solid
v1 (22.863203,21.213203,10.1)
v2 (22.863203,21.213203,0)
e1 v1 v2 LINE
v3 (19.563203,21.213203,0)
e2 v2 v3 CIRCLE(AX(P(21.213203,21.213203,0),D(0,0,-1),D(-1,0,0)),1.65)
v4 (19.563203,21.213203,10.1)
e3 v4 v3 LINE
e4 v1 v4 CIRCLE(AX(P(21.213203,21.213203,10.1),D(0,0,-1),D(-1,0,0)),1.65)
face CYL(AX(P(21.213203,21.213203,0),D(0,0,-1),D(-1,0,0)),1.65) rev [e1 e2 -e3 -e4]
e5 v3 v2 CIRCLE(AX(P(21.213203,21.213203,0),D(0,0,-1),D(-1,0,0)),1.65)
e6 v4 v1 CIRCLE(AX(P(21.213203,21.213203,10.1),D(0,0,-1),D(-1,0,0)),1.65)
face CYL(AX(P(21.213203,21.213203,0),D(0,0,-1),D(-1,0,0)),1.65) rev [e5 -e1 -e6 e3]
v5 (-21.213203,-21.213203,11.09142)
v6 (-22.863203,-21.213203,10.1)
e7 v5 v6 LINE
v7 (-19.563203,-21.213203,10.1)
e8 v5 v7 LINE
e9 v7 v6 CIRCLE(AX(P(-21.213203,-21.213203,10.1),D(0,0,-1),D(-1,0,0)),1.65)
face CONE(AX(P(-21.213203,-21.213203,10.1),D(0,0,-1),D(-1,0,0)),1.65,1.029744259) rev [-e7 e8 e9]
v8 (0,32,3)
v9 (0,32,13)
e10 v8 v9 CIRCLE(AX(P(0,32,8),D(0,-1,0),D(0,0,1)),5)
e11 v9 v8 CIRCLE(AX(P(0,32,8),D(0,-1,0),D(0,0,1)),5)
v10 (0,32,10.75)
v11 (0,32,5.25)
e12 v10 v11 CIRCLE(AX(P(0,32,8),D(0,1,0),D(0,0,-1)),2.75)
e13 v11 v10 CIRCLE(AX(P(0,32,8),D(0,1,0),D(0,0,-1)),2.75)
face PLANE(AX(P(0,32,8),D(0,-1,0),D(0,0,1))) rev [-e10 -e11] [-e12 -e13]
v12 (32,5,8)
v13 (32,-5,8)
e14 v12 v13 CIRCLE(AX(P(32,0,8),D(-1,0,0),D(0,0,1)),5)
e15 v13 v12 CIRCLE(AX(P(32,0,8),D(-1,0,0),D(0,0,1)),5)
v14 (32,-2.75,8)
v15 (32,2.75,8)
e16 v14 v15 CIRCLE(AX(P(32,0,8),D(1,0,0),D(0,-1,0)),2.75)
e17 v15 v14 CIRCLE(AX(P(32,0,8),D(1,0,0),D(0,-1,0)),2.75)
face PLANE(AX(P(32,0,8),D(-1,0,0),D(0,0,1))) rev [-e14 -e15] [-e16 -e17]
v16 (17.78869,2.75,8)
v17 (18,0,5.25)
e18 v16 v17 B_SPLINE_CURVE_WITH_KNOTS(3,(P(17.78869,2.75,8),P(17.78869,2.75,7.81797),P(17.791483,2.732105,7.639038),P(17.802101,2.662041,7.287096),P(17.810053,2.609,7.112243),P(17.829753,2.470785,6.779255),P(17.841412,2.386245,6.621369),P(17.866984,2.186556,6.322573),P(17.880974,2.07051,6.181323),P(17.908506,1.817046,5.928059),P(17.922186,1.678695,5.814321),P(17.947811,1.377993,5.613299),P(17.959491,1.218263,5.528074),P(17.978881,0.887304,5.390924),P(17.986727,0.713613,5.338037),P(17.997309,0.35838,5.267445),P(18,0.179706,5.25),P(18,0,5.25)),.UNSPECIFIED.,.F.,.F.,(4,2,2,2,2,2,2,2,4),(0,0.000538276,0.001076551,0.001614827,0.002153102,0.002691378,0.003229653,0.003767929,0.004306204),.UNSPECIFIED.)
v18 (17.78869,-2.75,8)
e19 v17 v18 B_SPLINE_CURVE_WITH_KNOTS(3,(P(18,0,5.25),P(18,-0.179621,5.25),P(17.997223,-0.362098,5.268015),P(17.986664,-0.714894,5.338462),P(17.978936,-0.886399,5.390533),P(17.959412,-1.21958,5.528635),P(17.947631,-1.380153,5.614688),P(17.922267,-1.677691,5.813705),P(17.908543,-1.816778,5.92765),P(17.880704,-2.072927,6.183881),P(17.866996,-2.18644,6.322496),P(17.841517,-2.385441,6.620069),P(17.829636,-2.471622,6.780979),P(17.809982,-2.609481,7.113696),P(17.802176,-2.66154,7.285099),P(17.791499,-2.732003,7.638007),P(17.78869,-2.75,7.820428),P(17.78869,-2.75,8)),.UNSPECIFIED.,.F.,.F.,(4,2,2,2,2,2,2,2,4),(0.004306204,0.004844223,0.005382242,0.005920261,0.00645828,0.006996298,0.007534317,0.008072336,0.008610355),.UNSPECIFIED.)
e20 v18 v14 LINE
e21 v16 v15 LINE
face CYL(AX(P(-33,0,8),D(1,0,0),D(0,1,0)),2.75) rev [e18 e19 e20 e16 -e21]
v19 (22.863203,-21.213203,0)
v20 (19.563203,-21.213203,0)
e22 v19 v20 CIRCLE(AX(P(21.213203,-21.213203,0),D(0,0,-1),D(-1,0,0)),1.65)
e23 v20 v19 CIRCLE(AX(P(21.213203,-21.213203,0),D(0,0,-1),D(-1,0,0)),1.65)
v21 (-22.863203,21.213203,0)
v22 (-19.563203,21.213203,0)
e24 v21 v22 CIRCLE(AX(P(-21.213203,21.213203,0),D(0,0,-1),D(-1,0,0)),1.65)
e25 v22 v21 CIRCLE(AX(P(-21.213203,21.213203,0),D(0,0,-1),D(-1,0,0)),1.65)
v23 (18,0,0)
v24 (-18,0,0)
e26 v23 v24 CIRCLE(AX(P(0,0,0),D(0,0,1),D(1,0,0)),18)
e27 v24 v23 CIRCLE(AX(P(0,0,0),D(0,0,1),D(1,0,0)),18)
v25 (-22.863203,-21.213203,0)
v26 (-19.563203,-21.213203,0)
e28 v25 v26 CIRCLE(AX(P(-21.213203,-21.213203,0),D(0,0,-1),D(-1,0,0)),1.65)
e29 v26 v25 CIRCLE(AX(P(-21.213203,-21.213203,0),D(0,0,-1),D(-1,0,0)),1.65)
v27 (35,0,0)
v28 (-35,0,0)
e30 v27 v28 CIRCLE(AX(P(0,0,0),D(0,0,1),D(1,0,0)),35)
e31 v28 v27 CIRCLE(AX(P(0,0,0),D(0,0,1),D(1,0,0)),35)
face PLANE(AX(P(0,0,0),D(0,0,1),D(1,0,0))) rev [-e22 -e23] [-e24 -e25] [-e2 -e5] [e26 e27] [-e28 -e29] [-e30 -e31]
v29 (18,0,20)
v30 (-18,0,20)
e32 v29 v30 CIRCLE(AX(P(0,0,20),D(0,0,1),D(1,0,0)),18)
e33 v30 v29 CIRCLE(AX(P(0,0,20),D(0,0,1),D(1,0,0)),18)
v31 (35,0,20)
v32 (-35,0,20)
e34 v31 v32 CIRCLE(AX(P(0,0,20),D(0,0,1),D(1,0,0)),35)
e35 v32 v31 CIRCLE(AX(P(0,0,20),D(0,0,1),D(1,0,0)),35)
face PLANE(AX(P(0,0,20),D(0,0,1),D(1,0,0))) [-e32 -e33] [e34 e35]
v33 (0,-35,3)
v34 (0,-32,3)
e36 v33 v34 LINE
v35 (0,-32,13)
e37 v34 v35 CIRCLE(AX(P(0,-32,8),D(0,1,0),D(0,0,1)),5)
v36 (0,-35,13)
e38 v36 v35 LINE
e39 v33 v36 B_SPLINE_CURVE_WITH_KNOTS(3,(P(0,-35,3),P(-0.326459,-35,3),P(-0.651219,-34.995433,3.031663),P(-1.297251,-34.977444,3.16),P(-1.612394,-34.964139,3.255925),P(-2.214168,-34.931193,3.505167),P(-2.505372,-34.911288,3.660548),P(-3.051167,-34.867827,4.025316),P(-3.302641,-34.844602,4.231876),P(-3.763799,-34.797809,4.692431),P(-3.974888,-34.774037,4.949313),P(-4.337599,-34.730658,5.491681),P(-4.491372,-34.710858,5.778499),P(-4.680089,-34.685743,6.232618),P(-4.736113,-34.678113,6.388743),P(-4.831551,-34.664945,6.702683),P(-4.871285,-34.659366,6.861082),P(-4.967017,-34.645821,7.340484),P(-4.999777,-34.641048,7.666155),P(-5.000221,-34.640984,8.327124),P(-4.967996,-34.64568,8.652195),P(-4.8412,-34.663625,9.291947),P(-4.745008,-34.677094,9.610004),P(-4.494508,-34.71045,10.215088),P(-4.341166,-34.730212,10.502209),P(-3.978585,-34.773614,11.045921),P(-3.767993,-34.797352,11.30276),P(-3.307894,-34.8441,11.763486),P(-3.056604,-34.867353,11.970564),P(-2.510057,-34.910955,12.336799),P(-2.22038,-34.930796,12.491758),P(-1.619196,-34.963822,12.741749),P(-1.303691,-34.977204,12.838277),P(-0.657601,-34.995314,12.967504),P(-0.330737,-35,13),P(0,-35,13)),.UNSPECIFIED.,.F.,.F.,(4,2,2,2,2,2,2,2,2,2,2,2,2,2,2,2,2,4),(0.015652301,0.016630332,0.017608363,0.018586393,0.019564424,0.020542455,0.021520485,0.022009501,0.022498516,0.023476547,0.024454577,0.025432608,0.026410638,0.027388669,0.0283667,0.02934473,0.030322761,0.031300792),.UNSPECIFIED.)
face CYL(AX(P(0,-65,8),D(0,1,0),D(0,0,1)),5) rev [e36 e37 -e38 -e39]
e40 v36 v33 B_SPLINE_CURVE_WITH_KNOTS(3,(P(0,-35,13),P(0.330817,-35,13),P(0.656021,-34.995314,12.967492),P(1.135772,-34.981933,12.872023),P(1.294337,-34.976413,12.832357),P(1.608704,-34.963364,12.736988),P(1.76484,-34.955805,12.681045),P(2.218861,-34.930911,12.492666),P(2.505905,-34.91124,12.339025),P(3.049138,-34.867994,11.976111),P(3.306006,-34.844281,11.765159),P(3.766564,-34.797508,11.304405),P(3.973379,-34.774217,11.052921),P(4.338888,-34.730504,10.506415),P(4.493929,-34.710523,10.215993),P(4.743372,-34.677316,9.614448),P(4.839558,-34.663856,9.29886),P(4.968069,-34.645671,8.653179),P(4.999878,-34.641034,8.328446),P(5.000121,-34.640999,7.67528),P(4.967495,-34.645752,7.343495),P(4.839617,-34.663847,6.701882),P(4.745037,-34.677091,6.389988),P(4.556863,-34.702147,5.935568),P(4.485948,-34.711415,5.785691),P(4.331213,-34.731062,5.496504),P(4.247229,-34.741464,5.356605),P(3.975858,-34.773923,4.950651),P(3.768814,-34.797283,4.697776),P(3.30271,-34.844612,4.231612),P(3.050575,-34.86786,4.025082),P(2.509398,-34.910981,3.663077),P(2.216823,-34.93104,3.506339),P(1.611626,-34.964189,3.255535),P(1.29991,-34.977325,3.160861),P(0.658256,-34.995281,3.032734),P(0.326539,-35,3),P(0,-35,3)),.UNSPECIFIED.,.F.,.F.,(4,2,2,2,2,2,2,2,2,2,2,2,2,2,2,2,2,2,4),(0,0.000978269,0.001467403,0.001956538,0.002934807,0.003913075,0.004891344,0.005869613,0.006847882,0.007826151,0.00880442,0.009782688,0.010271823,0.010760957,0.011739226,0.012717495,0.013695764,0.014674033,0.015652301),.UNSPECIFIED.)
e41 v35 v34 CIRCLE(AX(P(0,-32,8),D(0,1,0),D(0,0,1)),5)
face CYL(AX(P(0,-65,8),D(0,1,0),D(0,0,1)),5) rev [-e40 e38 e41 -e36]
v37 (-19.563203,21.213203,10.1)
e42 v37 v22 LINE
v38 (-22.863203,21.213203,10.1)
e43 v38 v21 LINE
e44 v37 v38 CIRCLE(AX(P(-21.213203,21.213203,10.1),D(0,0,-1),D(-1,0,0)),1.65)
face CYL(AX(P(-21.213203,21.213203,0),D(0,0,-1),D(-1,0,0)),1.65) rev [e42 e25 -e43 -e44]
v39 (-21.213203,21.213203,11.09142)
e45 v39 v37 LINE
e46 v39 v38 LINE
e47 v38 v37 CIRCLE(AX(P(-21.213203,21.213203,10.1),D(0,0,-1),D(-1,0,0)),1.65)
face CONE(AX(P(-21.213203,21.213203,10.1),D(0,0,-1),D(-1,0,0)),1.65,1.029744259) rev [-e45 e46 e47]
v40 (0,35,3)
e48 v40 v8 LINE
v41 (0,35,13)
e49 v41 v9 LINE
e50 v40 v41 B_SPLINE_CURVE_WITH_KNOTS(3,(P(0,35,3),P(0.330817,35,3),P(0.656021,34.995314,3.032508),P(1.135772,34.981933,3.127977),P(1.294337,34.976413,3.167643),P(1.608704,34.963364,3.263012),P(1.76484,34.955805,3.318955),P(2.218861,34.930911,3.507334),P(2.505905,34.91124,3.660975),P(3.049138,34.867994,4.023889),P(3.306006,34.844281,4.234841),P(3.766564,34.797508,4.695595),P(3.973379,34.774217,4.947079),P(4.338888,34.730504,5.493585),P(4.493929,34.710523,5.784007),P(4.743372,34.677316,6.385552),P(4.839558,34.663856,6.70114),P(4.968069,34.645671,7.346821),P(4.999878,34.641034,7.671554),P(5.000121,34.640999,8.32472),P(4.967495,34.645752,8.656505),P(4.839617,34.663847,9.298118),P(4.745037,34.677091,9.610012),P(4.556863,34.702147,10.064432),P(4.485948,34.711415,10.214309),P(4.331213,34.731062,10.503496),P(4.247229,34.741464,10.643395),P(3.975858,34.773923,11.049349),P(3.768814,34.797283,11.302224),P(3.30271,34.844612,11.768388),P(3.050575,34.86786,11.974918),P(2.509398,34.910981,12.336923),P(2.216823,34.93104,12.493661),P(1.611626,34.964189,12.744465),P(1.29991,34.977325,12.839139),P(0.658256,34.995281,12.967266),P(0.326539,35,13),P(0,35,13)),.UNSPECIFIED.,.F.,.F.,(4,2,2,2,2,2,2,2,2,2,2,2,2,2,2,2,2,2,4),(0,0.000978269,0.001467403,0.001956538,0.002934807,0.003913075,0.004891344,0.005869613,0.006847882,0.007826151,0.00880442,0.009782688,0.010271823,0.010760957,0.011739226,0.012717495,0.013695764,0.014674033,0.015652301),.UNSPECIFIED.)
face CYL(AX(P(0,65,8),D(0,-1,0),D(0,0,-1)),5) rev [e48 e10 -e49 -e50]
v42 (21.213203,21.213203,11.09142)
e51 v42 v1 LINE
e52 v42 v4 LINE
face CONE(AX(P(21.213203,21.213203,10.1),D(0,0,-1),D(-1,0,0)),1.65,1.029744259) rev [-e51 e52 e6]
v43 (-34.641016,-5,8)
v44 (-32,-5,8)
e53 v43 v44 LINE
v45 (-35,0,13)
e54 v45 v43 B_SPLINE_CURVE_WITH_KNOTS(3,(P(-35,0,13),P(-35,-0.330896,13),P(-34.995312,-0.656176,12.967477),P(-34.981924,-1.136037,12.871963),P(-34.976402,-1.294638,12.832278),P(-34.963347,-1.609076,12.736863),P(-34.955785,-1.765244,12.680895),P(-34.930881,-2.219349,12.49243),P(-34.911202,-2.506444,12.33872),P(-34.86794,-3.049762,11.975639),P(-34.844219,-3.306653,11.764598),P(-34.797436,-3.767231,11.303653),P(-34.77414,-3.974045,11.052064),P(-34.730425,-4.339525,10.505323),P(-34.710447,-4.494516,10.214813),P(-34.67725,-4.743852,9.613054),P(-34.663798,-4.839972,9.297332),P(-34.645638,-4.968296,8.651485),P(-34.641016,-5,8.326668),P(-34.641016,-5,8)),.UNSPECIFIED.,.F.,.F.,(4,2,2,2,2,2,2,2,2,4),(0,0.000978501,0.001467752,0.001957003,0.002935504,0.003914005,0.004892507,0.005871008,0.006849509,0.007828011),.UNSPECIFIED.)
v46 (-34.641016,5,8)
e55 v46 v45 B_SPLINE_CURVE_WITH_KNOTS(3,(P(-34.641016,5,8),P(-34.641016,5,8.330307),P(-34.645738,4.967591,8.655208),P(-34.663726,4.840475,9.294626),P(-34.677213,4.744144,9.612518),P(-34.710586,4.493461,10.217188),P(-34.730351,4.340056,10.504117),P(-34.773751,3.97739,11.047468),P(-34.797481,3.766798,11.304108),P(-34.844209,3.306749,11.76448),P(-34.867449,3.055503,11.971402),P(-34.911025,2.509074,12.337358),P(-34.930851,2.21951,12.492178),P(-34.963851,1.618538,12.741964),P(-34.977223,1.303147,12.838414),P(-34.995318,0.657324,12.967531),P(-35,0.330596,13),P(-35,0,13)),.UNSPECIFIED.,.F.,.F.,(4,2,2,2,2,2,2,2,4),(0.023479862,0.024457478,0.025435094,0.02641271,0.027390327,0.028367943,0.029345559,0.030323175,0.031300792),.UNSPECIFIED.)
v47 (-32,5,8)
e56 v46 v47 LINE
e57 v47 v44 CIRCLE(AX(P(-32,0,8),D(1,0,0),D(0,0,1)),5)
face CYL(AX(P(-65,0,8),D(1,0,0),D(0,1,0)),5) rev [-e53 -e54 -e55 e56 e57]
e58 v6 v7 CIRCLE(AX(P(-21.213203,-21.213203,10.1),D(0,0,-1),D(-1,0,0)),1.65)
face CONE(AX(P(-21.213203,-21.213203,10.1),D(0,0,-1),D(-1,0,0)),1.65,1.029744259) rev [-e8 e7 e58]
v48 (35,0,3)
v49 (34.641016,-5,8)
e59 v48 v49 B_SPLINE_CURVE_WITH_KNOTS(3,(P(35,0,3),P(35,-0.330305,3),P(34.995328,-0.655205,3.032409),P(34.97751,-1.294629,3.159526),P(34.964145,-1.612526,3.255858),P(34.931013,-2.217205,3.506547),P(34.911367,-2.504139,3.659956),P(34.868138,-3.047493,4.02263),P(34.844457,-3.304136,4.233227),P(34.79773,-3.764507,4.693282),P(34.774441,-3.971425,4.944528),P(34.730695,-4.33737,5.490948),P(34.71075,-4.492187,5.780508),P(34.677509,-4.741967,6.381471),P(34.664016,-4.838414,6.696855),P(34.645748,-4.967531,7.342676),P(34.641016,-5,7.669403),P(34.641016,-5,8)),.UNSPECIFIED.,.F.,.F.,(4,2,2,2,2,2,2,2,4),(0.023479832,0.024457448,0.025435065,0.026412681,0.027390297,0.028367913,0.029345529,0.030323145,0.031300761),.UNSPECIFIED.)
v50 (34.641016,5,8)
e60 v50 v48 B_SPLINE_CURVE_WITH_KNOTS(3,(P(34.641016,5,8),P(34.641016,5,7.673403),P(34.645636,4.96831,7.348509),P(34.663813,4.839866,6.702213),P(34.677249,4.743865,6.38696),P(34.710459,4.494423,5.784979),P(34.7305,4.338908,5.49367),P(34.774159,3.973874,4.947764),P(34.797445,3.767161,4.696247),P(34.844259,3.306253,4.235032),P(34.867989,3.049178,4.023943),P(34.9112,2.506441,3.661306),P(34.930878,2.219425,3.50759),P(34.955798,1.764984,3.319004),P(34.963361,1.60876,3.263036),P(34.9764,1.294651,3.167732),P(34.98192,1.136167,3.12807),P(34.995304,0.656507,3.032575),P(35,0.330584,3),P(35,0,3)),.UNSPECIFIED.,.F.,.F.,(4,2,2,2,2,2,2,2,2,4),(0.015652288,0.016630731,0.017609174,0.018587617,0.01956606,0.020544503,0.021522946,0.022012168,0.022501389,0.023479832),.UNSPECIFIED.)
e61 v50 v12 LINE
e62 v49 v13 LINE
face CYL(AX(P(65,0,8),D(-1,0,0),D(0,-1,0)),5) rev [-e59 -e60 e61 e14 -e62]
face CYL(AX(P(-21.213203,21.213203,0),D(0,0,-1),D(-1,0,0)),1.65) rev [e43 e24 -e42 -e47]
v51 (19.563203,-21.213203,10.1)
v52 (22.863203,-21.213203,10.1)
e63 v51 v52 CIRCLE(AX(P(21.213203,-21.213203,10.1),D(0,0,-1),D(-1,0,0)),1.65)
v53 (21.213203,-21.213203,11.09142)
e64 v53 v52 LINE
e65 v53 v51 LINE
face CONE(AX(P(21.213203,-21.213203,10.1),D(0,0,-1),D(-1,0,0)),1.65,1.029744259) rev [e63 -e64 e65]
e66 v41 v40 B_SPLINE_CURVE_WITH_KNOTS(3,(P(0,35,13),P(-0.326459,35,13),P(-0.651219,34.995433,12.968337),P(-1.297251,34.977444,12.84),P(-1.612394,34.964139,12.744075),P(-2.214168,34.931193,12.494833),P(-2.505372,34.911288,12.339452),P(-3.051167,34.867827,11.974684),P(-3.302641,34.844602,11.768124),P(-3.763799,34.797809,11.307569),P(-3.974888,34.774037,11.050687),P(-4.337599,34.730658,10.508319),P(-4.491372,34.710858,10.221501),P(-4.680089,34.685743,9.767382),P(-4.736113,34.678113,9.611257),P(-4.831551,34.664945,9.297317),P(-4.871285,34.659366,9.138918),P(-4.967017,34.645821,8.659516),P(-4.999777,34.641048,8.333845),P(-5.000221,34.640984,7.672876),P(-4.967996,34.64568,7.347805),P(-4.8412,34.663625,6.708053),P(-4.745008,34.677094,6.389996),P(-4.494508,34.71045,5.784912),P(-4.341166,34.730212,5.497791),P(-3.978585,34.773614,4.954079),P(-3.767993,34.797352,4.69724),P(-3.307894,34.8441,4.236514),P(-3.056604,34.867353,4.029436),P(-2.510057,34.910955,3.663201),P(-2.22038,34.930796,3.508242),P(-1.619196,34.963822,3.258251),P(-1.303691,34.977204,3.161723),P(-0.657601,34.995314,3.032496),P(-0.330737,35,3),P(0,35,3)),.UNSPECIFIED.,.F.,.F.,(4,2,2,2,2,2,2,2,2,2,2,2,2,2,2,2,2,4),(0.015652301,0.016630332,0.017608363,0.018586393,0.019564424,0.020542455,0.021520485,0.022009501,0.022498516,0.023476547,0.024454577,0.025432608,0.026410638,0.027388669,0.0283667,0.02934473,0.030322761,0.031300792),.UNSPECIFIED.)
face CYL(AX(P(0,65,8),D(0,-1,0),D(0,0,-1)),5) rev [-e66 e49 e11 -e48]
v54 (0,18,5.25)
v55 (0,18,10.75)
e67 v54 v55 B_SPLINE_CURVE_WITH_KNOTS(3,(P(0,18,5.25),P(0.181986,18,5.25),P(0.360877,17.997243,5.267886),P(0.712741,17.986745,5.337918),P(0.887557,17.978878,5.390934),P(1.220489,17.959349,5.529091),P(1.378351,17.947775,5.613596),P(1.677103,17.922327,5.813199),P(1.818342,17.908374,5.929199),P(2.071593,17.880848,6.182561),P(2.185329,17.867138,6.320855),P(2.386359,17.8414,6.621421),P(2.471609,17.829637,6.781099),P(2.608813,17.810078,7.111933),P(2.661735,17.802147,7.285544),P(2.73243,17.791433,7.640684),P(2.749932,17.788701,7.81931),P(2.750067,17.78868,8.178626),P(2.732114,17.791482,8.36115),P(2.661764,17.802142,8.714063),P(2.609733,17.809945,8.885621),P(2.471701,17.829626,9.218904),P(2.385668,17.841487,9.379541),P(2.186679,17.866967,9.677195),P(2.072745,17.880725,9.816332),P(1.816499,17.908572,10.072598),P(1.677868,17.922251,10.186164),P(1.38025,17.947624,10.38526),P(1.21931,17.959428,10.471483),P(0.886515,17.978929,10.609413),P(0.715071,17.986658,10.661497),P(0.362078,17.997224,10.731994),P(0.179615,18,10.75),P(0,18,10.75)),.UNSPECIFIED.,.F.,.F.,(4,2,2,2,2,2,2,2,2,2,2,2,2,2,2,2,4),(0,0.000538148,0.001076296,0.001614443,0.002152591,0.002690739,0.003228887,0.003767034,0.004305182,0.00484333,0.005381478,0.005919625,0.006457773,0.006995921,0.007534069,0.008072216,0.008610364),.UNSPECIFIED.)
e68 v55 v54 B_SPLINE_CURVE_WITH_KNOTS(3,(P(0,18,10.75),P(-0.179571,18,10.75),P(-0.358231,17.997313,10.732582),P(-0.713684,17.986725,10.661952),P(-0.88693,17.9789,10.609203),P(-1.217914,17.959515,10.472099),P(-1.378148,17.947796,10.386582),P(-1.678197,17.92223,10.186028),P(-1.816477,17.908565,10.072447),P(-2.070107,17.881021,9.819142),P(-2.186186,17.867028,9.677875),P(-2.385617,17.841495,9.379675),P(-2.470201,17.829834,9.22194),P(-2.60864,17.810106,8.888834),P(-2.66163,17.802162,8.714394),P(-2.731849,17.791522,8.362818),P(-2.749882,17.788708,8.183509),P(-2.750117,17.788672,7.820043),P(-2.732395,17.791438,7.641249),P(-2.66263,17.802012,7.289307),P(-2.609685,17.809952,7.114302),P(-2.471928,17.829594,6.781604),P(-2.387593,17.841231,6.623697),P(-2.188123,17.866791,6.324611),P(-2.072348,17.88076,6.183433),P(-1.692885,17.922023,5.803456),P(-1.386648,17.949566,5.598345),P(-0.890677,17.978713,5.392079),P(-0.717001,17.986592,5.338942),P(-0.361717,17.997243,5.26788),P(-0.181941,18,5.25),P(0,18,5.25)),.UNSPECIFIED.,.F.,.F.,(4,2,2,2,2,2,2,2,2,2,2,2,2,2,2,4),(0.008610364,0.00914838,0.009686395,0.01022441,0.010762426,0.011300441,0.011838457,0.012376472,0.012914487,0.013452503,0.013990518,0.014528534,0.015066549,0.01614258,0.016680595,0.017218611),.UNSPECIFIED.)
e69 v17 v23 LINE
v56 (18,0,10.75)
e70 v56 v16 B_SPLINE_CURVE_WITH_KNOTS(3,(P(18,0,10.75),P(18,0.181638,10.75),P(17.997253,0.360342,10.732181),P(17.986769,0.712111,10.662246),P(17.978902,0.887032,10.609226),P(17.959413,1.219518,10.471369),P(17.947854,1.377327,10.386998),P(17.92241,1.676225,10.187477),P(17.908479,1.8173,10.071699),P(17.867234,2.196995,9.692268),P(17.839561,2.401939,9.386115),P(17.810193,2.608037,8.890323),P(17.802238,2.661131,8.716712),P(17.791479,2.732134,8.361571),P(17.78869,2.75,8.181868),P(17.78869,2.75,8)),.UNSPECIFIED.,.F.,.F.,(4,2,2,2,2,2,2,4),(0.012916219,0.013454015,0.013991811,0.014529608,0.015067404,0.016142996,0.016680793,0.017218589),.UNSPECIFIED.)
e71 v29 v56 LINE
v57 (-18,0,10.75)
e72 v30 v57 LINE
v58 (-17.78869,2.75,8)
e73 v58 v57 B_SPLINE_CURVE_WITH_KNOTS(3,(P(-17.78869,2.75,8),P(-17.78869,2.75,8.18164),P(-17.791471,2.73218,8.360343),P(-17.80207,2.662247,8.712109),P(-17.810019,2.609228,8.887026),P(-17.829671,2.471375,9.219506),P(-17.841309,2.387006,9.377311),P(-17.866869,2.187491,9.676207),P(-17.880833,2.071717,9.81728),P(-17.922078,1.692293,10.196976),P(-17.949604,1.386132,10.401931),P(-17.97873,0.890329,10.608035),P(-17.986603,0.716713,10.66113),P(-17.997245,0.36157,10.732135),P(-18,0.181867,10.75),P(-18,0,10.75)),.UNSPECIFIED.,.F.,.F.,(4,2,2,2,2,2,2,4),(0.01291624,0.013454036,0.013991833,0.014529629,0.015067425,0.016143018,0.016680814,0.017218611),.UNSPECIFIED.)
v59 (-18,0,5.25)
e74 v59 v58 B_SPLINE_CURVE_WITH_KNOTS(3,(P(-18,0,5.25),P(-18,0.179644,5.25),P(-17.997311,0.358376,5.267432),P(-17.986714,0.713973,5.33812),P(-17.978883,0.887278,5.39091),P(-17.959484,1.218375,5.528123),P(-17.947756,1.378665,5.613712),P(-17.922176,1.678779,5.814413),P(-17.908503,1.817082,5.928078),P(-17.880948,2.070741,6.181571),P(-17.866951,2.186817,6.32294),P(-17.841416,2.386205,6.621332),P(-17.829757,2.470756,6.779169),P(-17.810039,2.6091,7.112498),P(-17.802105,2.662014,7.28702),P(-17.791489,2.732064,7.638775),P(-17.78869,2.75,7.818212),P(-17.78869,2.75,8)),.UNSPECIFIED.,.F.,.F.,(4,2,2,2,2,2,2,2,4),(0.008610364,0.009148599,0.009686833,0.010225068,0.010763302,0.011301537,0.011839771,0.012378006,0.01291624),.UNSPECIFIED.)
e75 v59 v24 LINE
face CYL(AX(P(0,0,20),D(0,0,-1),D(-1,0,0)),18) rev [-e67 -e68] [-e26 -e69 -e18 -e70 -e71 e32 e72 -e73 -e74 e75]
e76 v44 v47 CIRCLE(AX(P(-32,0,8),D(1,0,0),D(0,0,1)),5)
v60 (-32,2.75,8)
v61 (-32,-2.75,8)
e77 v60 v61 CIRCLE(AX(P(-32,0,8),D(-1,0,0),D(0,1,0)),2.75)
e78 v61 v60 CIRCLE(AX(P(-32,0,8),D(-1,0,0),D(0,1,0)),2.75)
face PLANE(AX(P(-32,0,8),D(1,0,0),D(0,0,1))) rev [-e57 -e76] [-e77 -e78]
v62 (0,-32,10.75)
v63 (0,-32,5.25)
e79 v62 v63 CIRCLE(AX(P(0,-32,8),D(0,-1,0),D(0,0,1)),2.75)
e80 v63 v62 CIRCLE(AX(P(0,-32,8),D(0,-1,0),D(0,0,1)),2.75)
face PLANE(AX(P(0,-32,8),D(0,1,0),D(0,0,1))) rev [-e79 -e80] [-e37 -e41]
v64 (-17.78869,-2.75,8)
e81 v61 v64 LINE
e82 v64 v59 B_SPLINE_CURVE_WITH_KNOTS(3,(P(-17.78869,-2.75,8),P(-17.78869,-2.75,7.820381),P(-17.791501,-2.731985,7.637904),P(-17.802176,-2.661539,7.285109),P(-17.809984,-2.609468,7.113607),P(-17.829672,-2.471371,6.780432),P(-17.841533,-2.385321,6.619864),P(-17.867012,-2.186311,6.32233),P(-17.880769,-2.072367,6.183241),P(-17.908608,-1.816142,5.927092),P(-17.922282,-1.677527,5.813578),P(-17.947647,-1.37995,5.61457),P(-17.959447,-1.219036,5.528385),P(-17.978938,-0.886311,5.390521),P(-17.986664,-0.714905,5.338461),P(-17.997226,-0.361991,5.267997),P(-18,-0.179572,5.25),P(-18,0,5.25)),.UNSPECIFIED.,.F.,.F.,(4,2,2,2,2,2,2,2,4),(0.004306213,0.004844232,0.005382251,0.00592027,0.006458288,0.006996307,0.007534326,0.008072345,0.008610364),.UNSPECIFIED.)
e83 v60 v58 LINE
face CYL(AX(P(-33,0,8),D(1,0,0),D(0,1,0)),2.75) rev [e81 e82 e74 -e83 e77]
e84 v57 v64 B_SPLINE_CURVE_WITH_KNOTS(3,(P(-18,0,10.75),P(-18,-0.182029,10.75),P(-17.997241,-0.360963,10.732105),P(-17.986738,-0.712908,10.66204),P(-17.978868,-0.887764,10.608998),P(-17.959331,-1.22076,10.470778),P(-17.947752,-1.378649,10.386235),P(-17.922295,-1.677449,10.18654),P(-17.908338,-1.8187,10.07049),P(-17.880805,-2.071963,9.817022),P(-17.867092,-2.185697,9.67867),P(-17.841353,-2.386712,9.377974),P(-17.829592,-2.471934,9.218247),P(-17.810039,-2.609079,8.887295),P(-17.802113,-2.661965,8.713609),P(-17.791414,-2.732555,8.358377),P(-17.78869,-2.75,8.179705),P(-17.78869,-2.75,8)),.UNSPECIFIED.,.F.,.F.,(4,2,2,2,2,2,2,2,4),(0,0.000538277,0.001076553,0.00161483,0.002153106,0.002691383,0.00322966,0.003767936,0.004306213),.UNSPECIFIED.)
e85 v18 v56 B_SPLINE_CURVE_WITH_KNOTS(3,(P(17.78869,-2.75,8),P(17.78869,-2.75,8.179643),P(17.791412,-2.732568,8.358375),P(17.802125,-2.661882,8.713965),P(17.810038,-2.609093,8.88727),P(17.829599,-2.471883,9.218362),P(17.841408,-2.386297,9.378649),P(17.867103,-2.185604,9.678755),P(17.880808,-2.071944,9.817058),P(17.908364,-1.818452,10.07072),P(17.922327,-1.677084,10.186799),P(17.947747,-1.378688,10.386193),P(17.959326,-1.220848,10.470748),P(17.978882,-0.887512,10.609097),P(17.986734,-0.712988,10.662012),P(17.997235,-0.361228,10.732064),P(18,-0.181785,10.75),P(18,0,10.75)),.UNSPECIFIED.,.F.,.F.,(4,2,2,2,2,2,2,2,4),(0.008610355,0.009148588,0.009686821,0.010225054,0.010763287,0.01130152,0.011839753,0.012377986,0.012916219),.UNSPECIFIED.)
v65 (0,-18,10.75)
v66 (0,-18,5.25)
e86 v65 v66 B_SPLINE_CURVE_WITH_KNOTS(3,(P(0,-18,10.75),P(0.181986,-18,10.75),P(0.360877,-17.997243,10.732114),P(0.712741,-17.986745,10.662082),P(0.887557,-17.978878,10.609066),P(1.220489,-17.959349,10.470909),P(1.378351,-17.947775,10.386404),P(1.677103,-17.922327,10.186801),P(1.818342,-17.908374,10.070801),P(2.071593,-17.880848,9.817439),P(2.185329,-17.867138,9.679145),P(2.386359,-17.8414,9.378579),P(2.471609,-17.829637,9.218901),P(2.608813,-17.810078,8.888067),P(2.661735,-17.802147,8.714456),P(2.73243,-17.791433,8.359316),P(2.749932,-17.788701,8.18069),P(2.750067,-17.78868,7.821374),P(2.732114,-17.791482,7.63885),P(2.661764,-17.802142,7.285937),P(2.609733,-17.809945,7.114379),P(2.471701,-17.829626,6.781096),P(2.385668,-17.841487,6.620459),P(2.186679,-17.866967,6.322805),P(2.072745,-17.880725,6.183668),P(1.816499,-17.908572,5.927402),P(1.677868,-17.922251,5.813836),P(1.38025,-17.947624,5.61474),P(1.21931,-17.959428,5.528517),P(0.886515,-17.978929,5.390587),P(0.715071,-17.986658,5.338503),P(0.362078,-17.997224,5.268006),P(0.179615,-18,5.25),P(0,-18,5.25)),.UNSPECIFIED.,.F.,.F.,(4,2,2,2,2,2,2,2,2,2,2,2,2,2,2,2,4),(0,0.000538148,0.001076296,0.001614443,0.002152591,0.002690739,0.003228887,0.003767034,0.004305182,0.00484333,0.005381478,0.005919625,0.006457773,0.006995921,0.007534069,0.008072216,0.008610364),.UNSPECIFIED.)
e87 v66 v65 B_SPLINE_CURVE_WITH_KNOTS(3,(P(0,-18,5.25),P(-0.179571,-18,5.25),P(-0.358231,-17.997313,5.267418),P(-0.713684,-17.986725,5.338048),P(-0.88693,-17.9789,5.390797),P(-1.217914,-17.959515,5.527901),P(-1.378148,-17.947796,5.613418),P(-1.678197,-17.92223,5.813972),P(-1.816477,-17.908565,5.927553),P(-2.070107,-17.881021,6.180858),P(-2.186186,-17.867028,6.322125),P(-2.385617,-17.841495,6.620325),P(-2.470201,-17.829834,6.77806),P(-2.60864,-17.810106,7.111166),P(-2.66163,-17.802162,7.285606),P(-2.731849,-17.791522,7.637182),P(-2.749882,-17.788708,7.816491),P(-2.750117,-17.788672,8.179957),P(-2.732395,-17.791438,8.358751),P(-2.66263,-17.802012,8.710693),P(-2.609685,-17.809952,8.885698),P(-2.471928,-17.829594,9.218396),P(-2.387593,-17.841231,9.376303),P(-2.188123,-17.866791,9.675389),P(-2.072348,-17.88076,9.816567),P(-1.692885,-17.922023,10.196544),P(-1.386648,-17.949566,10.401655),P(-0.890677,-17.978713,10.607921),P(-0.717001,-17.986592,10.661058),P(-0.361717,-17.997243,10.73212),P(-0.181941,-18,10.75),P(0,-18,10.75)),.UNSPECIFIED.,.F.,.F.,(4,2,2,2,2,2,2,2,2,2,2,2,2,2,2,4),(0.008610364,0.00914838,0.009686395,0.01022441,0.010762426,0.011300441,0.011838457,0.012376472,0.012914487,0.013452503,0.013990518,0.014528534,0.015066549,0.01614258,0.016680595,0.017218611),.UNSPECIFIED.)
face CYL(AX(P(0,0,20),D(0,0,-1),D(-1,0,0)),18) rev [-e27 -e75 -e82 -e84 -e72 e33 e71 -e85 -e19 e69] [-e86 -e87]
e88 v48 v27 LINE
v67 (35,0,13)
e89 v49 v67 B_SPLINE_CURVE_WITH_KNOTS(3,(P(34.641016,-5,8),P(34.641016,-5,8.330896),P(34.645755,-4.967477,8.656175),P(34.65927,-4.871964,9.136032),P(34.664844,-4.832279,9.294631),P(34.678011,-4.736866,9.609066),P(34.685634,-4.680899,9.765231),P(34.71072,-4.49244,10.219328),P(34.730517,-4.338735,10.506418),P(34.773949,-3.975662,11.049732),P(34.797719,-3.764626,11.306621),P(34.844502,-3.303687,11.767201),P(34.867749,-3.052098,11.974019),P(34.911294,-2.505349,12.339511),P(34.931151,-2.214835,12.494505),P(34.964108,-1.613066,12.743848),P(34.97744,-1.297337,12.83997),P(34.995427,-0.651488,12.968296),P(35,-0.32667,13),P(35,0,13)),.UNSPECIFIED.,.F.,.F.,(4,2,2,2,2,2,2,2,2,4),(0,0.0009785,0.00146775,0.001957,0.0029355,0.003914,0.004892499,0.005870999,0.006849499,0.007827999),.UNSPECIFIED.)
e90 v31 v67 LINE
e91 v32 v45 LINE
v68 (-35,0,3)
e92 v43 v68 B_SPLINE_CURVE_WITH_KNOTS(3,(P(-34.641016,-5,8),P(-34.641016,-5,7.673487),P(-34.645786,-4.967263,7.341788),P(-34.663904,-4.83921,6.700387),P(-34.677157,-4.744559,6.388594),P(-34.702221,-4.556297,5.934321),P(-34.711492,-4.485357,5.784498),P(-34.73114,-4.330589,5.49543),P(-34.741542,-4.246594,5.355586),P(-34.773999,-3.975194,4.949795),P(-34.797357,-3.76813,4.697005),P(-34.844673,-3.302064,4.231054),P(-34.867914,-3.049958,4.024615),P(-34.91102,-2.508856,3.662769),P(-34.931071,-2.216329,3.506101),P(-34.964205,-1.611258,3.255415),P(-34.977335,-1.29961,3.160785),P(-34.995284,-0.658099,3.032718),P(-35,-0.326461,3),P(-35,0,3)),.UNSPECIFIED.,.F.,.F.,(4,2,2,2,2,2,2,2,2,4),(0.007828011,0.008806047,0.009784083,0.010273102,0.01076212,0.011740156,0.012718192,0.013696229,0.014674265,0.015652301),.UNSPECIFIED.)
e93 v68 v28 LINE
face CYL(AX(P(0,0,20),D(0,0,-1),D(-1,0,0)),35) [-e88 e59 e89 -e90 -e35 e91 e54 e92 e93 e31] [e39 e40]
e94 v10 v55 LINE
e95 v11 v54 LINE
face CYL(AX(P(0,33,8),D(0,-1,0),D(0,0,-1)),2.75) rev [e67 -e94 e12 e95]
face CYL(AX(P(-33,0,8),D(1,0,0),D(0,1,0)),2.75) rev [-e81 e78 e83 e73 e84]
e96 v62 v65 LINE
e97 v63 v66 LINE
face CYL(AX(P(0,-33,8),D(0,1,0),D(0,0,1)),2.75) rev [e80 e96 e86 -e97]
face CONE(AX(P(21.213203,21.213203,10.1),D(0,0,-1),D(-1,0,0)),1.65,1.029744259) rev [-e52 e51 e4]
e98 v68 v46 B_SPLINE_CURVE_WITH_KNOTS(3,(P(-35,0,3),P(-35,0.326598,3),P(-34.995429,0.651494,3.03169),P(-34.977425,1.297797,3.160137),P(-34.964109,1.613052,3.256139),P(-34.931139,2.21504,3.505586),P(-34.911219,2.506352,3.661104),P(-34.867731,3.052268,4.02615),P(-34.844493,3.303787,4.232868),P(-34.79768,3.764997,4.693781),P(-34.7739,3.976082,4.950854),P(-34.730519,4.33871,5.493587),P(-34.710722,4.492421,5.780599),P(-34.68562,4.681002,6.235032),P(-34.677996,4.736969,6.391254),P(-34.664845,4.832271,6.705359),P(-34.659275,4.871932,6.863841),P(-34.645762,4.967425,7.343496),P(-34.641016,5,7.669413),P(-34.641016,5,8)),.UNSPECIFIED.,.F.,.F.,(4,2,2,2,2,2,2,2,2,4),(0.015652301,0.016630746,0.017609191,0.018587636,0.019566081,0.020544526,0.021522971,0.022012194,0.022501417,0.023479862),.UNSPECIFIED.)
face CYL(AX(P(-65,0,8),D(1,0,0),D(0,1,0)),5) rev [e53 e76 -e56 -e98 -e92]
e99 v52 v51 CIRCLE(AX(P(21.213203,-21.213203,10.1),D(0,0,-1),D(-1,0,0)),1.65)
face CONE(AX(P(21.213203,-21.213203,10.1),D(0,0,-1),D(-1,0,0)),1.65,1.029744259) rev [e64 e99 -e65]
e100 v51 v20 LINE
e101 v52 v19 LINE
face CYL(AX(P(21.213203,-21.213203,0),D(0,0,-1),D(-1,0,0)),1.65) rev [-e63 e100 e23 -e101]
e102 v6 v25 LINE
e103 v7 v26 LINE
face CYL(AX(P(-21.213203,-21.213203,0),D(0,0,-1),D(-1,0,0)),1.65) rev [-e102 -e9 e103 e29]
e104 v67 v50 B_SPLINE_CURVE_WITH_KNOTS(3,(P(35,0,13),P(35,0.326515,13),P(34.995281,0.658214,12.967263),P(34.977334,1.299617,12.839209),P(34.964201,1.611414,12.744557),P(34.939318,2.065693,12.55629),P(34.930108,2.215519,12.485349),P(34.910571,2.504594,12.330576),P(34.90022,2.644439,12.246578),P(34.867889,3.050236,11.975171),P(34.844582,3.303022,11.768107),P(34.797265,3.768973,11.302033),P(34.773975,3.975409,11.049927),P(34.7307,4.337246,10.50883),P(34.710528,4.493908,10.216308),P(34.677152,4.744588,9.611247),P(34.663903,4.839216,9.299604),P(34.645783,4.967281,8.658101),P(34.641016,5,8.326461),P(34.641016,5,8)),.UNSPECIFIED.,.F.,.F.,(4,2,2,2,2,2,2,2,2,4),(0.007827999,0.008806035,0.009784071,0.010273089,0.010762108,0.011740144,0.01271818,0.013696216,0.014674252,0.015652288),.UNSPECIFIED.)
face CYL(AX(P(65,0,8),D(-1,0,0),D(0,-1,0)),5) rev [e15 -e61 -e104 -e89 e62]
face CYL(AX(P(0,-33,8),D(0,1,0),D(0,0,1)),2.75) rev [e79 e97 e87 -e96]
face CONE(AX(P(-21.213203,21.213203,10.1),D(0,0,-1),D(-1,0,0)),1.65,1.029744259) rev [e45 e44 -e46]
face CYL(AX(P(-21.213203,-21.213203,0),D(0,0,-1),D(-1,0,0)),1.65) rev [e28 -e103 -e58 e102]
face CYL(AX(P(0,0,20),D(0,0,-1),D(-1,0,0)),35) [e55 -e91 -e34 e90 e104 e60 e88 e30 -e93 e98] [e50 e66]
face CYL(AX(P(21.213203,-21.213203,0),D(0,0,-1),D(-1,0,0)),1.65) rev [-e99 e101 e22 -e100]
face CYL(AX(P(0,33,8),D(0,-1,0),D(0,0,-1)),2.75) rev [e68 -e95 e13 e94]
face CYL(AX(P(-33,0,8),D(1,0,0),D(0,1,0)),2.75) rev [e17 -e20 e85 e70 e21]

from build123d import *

# Parameters (mm, degrees)
SKETCH_1_R               = 35
SKETCH_1_R_2             = 18
EXTRUDE_1_DEPTH          = 20
SKETCH_5_R               = 2.75
CUT_EXTRUDE_1_DEPTH      = 33
CUT_EXTRUDE_START        = -32
SKETCH_6_R               = 5
CUT_EXTRUDE_3_DEPTH      = 33
PATTERN_CIRCULAR_1_COUNT = 4
PATTERN_CIRCULAR_2_COUNT = 4


with BuildPart() as part:
    # 草图1 → 凸台-拉伸1 (new body)
    with BuildSketch(Plane.XY):
        Circle(SKETCH_1_R)
        Circle(SKETCH_1_R_2, mode=Mode.SUBTRACT)
    extrude(amount=EXTRUDE_1_DEPTH)

    # 草图5 → 切除-拉伸1 (cut)
    with BuildSketch(Plane(origin=(0, 0, 0), x_dir=(1, 0, 0), z_dir=(0, 1, 0))):
        with Locations(Location((0, -8, 0), (0, 0, 270))):
            Circle(SKETCH_5_R)
    cut_extrude_1 = extrude(amount=-CUT_EXTRUDE_1_DEPTH, mode=Mode.SUBTRACT)

    # 草图6 → 切除-拉伸3 (cut)
    with BuildSketch(Plane(origin=(0, 0, 0), x_dir=(1, 0, 0), z_dir=(0, 1, 0)).offset(CUT_EXTRUDE_START)):
        with Locations(Location((0, -8, 0), (0, 0, 270))):
            Circle(SKETCH_6_R)
    cut_extrude_3 = extrude(amount=-CUT_EXTRUDE_3_DEPTH, mode=Mode.SUBTRACT)

    # 阵列(圆周)1: 切除-拉伸1, 切除-拉伸3 ×4 about axis
    pattern_circular_1_axis = Axis((0, 0, 0), (0, 0, 1))
    add([cut_extrude_1.rotate(pattern_circular_1_axis, i * 360 / PATTERN_CIRCULAR_1_COUNT) for i in range(1, PATTERN_CIRCULAR_1_COUNT)], mode=Mode.SUBTRACT)
    add([cut_extrude_3.rotate(pattern_circular_1_axis, i * 360 / PATTERN_CIRCULAR_1_COUNT) for i in range(1, PATTERN_CIRCULAR_1_COUNT)], mode=Mode.SUBTRACT)

    # 草图7 → M4x0.7 螺纹孔1 (revolve, cut)
    with BuildSketch(Plane(origin=(21.213203436, 21.213203436, 0), x_dir=(0, 1, 0), z_dir=(1, 0, 0))):
        Polygon((0, 0), (0, 11.091420021), (1.65, 10.1), (1.65, 0), align=None)
    m4x0_7_1 = revolve(axis=Axis((21.213203436, 21.213203436, -6.35), (0, 0, 1)), mode=Mode.SUBTRACT)

    # 阵列(圆周)2: M4x0.7 螺纹孔1 ×4 about axis
    pattern_circular_2_axis = Axis((0, 0, 0), (0, 0, 1))
    for i in range(1, PATTERN_CIRCULAR_2_COUNT):
        add(m4x0_7_1.rotate(pattern_circular_2_axis, i * 360 / PATTERN_CIRCULAR_2_COUNT), mode=Mode.SUBTRACT)


solid = part.part
